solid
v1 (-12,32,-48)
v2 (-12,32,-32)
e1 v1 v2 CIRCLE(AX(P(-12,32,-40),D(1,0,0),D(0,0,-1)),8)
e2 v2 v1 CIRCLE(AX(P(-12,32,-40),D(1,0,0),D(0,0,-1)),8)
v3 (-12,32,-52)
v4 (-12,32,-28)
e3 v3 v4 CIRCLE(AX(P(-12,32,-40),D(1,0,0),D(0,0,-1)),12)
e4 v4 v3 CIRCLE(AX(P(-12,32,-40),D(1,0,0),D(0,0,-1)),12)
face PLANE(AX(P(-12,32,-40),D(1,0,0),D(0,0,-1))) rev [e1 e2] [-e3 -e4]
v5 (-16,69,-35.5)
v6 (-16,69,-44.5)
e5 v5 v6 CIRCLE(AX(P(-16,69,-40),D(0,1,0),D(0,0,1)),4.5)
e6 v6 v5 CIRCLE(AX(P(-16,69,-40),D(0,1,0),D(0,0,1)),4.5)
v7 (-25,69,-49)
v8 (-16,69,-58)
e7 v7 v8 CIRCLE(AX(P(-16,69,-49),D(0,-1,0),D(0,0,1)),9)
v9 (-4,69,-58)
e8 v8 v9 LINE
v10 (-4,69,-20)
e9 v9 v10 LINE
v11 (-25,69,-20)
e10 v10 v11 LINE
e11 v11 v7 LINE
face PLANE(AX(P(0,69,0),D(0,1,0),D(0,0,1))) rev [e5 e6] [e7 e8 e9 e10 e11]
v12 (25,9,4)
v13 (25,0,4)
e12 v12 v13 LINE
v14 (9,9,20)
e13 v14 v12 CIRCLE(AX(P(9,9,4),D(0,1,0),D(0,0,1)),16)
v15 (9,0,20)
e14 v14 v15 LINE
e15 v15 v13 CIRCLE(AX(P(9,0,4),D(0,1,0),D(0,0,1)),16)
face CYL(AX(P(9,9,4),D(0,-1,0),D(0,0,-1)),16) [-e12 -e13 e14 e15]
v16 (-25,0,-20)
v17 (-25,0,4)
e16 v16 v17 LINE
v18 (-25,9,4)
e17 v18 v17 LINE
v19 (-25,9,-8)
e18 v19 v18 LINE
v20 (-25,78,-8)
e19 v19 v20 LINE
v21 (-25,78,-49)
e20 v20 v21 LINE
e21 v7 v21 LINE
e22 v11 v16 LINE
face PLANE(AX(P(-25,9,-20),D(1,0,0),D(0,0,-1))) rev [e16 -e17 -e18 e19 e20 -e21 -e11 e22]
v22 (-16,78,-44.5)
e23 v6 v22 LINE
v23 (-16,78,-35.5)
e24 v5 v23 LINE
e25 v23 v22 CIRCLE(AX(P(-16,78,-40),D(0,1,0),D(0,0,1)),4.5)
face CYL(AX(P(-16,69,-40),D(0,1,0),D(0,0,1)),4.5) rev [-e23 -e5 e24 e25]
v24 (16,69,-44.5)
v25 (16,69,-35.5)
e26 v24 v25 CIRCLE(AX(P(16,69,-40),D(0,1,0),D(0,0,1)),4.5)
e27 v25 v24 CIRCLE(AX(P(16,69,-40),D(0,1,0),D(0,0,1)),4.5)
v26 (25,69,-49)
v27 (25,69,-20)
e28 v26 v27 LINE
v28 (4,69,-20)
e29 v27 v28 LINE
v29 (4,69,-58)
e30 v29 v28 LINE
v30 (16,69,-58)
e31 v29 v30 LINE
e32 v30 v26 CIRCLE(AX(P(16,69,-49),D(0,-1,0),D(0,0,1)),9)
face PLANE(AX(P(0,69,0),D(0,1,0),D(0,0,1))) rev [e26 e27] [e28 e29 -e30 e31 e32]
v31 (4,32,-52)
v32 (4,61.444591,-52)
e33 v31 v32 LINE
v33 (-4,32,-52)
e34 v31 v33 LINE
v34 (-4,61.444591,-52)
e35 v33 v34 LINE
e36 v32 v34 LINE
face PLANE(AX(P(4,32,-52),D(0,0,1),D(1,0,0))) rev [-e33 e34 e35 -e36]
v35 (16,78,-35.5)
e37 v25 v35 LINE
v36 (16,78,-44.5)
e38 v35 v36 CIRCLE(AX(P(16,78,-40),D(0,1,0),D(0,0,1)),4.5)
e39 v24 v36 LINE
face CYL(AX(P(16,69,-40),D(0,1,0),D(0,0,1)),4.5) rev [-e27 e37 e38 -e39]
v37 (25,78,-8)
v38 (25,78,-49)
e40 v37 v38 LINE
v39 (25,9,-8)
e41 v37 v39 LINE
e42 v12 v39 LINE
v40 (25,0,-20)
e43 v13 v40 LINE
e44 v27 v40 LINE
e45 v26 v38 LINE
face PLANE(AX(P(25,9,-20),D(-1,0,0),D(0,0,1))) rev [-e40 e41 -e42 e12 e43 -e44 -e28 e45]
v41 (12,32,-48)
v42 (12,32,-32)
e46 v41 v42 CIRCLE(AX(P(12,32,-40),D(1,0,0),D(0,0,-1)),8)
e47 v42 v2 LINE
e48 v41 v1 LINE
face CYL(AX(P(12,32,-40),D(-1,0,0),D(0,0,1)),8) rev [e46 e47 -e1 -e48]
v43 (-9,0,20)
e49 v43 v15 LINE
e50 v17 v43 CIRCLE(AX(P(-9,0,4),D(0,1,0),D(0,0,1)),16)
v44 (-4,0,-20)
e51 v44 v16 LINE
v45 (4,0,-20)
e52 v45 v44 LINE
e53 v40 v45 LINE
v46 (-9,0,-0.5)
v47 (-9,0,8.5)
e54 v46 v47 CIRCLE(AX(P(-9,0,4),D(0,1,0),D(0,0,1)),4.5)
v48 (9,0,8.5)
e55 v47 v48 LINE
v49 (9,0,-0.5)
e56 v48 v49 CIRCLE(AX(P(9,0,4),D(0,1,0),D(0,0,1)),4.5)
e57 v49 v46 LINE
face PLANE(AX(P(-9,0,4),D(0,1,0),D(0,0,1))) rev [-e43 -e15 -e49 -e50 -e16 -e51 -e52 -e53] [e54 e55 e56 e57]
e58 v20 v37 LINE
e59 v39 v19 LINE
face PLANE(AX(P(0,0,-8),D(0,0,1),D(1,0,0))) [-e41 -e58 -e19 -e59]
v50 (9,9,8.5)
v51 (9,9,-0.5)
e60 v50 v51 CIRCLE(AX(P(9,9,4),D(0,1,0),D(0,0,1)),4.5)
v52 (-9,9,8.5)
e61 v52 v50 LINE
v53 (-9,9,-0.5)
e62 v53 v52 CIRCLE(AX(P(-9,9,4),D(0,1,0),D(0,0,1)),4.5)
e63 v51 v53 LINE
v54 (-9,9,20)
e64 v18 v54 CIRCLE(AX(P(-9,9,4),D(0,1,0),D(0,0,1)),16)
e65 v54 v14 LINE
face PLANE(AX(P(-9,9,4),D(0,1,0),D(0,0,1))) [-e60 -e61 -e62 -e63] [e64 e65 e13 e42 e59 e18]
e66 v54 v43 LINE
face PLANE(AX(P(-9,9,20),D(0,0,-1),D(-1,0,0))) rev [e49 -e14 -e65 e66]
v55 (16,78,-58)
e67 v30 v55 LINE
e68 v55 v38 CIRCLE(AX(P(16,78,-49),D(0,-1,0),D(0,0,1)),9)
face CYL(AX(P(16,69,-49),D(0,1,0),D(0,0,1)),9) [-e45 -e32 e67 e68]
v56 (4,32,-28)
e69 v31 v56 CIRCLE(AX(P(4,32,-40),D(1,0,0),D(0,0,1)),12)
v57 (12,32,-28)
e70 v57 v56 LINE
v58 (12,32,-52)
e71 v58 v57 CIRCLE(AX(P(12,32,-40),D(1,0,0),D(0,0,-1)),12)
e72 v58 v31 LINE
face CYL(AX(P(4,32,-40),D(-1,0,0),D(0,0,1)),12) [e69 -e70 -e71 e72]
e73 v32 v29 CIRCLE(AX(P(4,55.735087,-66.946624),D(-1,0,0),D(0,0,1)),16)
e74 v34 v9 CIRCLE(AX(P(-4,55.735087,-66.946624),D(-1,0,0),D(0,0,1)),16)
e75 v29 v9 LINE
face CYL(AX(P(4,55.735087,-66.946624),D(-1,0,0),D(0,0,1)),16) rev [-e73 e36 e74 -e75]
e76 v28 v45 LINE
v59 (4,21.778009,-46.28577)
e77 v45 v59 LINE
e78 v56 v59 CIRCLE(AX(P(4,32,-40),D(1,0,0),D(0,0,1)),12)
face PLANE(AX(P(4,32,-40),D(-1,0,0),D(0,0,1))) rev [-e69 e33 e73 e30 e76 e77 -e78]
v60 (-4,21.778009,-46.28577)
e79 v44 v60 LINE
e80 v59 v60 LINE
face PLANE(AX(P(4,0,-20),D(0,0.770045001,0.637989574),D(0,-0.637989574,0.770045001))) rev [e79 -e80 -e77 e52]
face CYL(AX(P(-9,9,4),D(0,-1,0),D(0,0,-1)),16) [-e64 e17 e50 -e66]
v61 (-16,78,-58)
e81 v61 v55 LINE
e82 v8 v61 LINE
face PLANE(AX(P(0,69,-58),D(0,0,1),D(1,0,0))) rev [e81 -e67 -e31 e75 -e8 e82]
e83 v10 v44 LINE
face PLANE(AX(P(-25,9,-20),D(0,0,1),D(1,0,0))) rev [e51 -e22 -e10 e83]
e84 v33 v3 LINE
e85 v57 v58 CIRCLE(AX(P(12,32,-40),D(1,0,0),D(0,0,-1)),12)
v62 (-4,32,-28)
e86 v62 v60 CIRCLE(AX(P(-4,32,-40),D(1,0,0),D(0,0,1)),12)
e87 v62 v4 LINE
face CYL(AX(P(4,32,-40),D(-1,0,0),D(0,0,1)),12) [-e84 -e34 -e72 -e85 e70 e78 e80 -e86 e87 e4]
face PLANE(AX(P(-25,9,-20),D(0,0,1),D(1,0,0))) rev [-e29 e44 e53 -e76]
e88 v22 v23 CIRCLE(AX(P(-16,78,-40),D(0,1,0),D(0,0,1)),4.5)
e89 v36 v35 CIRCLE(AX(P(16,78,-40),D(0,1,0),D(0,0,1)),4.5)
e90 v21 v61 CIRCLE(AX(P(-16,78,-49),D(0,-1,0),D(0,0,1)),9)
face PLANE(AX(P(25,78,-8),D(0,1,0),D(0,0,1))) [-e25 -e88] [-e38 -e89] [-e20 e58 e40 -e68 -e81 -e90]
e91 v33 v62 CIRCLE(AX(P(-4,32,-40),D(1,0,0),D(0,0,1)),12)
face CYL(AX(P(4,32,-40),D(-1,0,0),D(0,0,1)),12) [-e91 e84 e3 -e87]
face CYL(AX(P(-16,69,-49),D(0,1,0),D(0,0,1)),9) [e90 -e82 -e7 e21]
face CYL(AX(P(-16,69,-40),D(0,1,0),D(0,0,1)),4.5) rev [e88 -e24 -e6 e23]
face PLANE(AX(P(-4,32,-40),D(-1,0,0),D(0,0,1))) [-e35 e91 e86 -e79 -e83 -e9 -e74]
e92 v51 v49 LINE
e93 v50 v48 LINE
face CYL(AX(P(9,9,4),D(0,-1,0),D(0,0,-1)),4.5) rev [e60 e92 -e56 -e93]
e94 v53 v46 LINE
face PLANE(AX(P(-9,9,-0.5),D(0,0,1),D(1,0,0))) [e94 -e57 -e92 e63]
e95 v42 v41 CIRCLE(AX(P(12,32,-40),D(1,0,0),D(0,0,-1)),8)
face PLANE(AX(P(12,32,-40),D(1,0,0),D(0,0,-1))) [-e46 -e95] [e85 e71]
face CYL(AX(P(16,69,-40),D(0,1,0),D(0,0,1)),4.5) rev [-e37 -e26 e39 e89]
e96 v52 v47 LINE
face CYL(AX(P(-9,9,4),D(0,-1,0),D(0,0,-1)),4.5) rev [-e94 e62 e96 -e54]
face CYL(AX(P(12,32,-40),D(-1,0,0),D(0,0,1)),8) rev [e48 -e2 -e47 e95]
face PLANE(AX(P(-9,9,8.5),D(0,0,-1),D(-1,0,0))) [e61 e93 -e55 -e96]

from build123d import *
from build123d.topology import SkipClean

# Parameters (mm, degrees)
BASE_FOOT_WITH_SLOT_DEPTH     = 9
UPRIGHT_WALL_SKETCH_W         = 50
UPRIGHT_WALL_SKETCH_H         = 69
UPRIGHT_WALL_DEPTH            = 12
TOP_FLANGE_SKETCH_R           = 4.5
TOP_FLANGE_WITH_2_HOLES_DEPTH = 9
SIDE_BOSS_SKETCH_R            = 12
SIDE_BOSS_SKETCH_R_2          = 8
SIDE_BOSS_DEPTH               = 12
BOSS_WEB_DEPTH                = 4
BOSS_BORE_SKETCH_R            = 8
BOSS_BORE_DEPTH               = 102.434708064


with BuildPart() as part:
    # Base Foot Sketch → Base Foot with Slot (new body)
    with BuildSketch(Plane(origin=(0, 0, 0), x_dir=(1, 0, 0), z_dir=(0, 1, 0))):
        with BuildLine():
            Line((-25, 20), (25, 20))
            Line((25, 20), (25, -4))
            ThreePointArc((25, -4), (20.313708499, -15.313708499), (9, -20))
            Line((9, -20), (-9, -20))
            ThreePointArc((-9, -20), (-20.313708499, -15.313708499), (-25, -4))
            Line((-25, -4), (-25, 20))
        make_face()
        with BuildLine():
            Line((-9, 0.5), (9, 0.5))
            ThreePointArc((9, 0.5), (13.5, -4), (9, -8.5))
            Line((9, -8.5), (-9, -8.5))
            ThreePointArc((-9, -8.5), (-13.5, -4), (-9, 0.5))
        make_face(mode=Mode.SUBTRACT)
    extrude(amount=BASE_FOOT_WITH_SLOT_DEPTH)

    # Upright Wall Sketch → Upright Wall (add)
    with BuildSketch(Plane(origin=(0, 0, -20), x_dir=(-1, 0, 0), z_dir=(0, 0, -1))):
        with Locations((0, 43.5)):
            Rectangle(UPRIGHT_WALL_SKETCH_W, UPRIGHT_WALL_SKETCH_H)
    extrude(amount=-UPRIGHT_WALL_DEPTH)

    # Top Flange Sketch → Top Flange with 2 Holes (add)
    with BuildSketch(Plane(origin=(0, 78, 0), x_dir=(1, 0, 0), z_dir=(0, 1, 0))):
        with BuildLine():
            Line((-25, 20), (-25, 49))
            ThreePointArc((-25, 49), (-22.363961031, 55.363961031), (-16, 58))
            Line((-16, 58), (16, 58))
            ThreePointArc((16, 58), (22.363961031, 55.363961031), (25, 49))
            Line((25, 49), (25, 20))
            Line((25, 20), (-25, 20))
        make_face()
        with Locations(Location((-16, 40, 0), (0, 0, 270))):
            Circle(TOP_FLANGE_SKETCH_R, mode=Mode.SUBTRACT)
        with Locations(Location((16, 40, 0), (0, 0, 270))):
            Circle(TOP_FLANGE_SKETCH_R, mode=Mode.SUBTRACT)
    extrude(amount=-TOP_FLANGE_WITH_2_HOLES_DEPTH)



with BuildPart() as body_2:
    # Side Boss Sketch → Side Boss (new, symmetric)
    with BuildSketch(Plane(origin=(0, 0, 0), x_dir=(0, 0, -1), z_dir=(1, 0, 0))):
        with Locations((40, 32)):
            Circle(SIDE_BOSS_SKETCH_R)
        with Locations((40, 32)):
            Circle(SIDE_BOSS_SKETCH_R_2, mode=Mode.SUBTRACT)
    extrude(amount=SIDE_BOSS_DEPTH, both=True)


with BuildPart() as part_1:
    with SkipClean():  # the faces are left unmerged after this step: merging them gives an invalid solid
        add(part.part)

        add(body_2.part)  # Boss Web merges body 2
        # Boss Web Sketch → Boss Web (add, symmetric)
        with BuildSketch(Plane(origin=(0, 0, 0), x_dir=(0, 0, -1), z_dir=(1, 0, 0))):
            with BuildLine():
                Line((52, 32), (52, 61.444590884))
                ThreePointArc((52, 61.444590884), (54.416944157, 65.68531935), (58, 69))
                Line((58, 69), (20, 69))
                Line((20, 69), (20, 0))
                Line((20, 0), (46.285769513, 21.778008921))
                ThreePointArc((46.285769513, 21.778008921), (50.474474549, 26.144627858), (52, 32))
            make_face()
        extrude(amount=BOSS_WEB_DEPTH, both=True)

    # Boss Bore Sketch → Boss Bore (cut, through all)
    with SkipClean():  # the faces are left unmerged after this step: merging them gives an invalid solid
        with BuildSketch(Plane.ZY.offset(4)):
            with Locations(Location((-40, 32, 0), (0, 0, 180))):
                Circle(BOSS_BORE_SKETCH_R)
        extrude(amount=-BOSS_BORE_DEPTH, mode=Mode.SUBTRACT)


solid = part_1.part
